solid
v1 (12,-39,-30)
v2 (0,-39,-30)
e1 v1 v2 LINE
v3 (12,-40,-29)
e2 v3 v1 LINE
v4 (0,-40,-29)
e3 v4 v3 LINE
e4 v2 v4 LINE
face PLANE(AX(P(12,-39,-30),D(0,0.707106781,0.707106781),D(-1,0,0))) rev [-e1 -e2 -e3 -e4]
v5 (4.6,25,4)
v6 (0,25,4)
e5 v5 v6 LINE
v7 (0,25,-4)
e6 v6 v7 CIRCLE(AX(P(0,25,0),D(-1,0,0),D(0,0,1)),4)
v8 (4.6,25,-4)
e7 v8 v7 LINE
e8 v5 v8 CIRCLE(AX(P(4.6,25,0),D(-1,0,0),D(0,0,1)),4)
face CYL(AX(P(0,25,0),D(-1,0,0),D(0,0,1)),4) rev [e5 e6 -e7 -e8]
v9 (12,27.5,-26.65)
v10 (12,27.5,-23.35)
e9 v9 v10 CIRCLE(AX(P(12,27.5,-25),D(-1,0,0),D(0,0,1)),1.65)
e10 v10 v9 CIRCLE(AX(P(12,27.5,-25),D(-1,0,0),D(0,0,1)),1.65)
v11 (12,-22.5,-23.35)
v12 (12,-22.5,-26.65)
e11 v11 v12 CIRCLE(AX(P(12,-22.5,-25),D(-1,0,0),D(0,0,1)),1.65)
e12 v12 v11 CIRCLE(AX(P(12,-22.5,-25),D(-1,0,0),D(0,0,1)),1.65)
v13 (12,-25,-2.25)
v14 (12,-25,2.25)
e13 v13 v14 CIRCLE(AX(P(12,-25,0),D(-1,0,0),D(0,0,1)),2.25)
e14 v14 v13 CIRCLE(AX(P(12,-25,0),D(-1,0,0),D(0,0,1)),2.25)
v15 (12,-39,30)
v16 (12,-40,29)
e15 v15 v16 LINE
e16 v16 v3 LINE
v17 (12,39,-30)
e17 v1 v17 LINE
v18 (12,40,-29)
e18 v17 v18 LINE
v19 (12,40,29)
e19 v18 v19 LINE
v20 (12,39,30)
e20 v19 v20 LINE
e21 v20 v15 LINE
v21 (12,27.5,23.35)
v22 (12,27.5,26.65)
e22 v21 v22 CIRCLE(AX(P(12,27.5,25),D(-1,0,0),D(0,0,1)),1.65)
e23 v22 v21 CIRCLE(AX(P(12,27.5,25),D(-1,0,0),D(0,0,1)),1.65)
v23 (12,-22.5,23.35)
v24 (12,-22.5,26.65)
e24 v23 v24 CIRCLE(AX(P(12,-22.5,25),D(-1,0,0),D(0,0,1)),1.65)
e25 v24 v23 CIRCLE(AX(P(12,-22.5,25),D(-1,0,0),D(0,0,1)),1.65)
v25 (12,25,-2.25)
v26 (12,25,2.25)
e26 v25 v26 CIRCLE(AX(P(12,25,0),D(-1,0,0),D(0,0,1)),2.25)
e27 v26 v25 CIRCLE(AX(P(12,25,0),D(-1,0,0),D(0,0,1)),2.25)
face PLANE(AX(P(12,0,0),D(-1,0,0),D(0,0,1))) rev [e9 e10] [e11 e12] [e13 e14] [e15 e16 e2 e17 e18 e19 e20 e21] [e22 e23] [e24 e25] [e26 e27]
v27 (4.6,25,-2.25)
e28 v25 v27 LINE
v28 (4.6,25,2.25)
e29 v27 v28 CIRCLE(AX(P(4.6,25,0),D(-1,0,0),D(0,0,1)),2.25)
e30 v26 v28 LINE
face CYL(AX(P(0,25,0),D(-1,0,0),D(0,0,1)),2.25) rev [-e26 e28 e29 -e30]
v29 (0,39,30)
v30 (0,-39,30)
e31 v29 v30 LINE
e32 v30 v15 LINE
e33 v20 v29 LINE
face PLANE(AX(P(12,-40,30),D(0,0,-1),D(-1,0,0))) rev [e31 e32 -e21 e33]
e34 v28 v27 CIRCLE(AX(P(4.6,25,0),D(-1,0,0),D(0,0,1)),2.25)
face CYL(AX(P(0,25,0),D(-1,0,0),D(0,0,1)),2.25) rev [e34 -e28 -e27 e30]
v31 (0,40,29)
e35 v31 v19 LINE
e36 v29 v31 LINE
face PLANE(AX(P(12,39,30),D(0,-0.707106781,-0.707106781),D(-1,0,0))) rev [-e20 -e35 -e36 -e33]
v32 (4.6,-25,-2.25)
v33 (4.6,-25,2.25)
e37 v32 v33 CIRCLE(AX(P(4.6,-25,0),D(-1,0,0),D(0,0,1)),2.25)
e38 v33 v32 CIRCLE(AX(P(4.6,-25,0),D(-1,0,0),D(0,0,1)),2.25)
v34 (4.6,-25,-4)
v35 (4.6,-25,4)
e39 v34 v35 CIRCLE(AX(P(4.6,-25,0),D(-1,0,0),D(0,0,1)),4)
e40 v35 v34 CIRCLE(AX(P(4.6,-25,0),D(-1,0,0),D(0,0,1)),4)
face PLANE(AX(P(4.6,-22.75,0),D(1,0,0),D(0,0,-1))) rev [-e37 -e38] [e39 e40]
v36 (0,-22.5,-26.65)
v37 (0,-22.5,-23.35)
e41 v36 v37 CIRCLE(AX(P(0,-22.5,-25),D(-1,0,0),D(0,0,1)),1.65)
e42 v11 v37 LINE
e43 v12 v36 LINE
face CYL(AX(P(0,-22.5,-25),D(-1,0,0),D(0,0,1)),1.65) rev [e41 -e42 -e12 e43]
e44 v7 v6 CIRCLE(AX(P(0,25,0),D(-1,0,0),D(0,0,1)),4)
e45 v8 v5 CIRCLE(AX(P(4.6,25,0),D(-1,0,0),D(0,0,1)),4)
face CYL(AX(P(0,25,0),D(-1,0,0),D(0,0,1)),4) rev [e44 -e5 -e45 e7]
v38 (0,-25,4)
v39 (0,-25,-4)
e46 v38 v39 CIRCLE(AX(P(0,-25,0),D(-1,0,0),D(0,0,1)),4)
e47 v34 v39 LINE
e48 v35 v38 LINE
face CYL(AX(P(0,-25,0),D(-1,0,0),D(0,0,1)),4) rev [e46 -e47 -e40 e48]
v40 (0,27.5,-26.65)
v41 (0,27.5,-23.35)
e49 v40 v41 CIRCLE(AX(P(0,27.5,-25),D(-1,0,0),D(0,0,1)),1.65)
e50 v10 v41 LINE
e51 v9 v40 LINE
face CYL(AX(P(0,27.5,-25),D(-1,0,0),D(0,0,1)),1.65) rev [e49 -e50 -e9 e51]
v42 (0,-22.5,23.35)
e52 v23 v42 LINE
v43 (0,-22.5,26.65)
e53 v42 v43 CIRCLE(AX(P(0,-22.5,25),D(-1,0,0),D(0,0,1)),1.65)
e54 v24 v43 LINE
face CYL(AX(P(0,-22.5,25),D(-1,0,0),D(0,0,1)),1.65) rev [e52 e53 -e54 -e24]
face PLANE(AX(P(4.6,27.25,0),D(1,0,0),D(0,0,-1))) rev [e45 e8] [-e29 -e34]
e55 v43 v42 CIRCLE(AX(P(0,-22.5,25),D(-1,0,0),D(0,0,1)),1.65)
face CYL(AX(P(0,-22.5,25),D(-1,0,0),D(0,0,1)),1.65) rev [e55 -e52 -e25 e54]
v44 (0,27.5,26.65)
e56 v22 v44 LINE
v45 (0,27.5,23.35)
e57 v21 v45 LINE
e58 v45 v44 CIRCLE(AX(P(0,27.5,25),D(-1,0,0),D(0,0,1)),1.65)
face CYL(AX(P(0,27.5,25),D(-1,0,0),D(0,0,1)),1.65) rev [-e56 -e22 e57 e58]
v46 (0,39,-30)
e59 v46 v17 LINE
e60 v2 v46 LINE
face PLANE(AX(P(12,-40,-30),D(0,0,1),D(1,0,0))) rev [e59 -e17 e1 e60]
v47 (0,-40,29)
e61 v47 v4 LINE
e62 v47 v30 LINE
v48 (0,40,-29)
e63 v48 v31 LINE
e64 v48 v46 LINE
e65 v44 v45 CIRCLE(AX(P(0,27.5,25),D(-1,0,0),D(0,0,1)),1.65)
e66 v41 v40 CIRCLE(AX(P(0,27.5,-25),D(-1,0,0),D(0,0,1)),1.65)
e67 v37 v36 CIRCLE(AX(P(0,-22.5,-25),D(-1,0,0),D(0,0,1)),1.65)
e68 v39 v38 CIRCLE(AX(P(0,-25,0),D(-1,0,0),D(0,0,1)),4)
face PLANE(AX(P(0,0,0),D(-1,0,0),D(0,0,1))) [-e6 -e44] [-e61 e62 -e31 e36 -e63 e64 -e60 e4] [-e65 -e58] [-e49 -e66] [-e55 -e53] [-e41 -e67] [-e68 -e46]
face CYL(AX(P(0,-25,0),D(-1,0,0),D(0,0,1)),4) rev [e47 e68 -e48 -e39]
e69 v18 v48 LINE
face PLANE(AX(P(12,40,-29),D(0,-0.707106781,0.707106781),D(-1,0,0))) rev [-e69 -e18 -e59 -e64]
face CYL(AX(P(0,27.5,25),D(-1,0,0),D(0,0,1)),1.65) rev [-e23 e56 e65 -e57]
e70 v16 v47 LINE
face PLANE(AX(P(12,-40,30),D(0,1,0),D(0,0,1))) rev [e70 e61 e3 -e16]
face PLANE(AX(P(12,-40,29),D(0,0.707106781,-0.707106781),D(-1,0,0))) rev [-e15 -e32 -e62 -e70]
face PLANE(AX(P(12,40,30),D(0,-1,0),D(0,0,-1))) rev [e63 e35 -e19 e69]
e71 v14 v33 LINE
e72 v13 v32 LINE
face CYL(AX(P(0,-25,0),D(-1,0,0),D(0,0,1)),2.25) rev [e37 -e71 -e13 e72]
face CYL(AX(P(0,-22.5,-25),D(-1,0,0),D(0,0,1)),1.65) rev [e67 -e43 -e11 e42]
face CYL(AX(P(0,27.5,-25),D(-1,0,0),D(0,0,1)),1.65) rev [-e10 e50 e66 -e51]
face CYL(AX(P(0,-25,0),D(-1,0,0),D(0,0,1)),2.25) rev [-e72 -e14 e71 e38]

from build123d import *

# Parameters (mm, degrees)
SKETCH1_W                                            = 60
SKETCH1_H                                            = 80
BOSS_EXTRUDE1_DEPTH                                  = 12
M4_TAPPED_HOLE1_D                                    = 3.3
CBORE_FOR_M4_HEXAGON_SOCKET_HEAD_CAP_SCR_D           = 4.5
CBORE_FOR_M4_HEXAGON_SOCKET_HEAD_CAP_SCR_CBORE_D     = 8
CBORE_FOR_M4_HEXAGON_SOCKET_HEAD_CAP_SCR_CBORE_DEPTH = 4.6
CHAMFER1_SIZE                                        = 1


with BuildPart() as part:
    # Sketch1 → Boss-Extrude1 (new body)
    with BuildSketch(Plane(origin=(0, 0, 0), x_dir=(0, 0, -1), z_dir=(1, 0, 0))):
        Rectangle(SKETCH1_W, SKETCH1_H)
    extrude(amount=BOSS_EXTRUDE1_DEPTH)

    # M4 Tapped Hole1 (through all)
    with Locations(Plane.ZY):
        with Locations((-25, 27.5), (-25, -22.5), (25, -22.5), (25, 27.5)):
            Hole(M4_TAPPED_HOLE1_D / 2)

    # CBORE for M4 Hexagon socket head cap screws1 (through all)
    with Locations(Plane.ZY):
        with Locations((0, -25), (0, 25)):
            CounterBoreHole(CBORE_FOR_M4_HEXAGON_SOCKET_HEAD_CAP_SCR_D / 2, CBORE_FOR_M4_HEXAGON_SOCKET_HEAD_CAP_SCR_CBORE_D / 2, CBORE_FOR_M4_HEXAGON_SOCKET_HEAD_CAP_SCR_CBORE_DEPTH)

    # Chamfer1
    chamfer1_edges = [part.edges().sort_by_distance(p)[0] for p in [
        (6, -40, -30),
        (6, -40, 30),
        (6, 40, 30),
        (6, 40, -30),
    ]]
    chamfer(chamfer1_edges, length=CHAMFER1_SIZE)


solid = part.part
